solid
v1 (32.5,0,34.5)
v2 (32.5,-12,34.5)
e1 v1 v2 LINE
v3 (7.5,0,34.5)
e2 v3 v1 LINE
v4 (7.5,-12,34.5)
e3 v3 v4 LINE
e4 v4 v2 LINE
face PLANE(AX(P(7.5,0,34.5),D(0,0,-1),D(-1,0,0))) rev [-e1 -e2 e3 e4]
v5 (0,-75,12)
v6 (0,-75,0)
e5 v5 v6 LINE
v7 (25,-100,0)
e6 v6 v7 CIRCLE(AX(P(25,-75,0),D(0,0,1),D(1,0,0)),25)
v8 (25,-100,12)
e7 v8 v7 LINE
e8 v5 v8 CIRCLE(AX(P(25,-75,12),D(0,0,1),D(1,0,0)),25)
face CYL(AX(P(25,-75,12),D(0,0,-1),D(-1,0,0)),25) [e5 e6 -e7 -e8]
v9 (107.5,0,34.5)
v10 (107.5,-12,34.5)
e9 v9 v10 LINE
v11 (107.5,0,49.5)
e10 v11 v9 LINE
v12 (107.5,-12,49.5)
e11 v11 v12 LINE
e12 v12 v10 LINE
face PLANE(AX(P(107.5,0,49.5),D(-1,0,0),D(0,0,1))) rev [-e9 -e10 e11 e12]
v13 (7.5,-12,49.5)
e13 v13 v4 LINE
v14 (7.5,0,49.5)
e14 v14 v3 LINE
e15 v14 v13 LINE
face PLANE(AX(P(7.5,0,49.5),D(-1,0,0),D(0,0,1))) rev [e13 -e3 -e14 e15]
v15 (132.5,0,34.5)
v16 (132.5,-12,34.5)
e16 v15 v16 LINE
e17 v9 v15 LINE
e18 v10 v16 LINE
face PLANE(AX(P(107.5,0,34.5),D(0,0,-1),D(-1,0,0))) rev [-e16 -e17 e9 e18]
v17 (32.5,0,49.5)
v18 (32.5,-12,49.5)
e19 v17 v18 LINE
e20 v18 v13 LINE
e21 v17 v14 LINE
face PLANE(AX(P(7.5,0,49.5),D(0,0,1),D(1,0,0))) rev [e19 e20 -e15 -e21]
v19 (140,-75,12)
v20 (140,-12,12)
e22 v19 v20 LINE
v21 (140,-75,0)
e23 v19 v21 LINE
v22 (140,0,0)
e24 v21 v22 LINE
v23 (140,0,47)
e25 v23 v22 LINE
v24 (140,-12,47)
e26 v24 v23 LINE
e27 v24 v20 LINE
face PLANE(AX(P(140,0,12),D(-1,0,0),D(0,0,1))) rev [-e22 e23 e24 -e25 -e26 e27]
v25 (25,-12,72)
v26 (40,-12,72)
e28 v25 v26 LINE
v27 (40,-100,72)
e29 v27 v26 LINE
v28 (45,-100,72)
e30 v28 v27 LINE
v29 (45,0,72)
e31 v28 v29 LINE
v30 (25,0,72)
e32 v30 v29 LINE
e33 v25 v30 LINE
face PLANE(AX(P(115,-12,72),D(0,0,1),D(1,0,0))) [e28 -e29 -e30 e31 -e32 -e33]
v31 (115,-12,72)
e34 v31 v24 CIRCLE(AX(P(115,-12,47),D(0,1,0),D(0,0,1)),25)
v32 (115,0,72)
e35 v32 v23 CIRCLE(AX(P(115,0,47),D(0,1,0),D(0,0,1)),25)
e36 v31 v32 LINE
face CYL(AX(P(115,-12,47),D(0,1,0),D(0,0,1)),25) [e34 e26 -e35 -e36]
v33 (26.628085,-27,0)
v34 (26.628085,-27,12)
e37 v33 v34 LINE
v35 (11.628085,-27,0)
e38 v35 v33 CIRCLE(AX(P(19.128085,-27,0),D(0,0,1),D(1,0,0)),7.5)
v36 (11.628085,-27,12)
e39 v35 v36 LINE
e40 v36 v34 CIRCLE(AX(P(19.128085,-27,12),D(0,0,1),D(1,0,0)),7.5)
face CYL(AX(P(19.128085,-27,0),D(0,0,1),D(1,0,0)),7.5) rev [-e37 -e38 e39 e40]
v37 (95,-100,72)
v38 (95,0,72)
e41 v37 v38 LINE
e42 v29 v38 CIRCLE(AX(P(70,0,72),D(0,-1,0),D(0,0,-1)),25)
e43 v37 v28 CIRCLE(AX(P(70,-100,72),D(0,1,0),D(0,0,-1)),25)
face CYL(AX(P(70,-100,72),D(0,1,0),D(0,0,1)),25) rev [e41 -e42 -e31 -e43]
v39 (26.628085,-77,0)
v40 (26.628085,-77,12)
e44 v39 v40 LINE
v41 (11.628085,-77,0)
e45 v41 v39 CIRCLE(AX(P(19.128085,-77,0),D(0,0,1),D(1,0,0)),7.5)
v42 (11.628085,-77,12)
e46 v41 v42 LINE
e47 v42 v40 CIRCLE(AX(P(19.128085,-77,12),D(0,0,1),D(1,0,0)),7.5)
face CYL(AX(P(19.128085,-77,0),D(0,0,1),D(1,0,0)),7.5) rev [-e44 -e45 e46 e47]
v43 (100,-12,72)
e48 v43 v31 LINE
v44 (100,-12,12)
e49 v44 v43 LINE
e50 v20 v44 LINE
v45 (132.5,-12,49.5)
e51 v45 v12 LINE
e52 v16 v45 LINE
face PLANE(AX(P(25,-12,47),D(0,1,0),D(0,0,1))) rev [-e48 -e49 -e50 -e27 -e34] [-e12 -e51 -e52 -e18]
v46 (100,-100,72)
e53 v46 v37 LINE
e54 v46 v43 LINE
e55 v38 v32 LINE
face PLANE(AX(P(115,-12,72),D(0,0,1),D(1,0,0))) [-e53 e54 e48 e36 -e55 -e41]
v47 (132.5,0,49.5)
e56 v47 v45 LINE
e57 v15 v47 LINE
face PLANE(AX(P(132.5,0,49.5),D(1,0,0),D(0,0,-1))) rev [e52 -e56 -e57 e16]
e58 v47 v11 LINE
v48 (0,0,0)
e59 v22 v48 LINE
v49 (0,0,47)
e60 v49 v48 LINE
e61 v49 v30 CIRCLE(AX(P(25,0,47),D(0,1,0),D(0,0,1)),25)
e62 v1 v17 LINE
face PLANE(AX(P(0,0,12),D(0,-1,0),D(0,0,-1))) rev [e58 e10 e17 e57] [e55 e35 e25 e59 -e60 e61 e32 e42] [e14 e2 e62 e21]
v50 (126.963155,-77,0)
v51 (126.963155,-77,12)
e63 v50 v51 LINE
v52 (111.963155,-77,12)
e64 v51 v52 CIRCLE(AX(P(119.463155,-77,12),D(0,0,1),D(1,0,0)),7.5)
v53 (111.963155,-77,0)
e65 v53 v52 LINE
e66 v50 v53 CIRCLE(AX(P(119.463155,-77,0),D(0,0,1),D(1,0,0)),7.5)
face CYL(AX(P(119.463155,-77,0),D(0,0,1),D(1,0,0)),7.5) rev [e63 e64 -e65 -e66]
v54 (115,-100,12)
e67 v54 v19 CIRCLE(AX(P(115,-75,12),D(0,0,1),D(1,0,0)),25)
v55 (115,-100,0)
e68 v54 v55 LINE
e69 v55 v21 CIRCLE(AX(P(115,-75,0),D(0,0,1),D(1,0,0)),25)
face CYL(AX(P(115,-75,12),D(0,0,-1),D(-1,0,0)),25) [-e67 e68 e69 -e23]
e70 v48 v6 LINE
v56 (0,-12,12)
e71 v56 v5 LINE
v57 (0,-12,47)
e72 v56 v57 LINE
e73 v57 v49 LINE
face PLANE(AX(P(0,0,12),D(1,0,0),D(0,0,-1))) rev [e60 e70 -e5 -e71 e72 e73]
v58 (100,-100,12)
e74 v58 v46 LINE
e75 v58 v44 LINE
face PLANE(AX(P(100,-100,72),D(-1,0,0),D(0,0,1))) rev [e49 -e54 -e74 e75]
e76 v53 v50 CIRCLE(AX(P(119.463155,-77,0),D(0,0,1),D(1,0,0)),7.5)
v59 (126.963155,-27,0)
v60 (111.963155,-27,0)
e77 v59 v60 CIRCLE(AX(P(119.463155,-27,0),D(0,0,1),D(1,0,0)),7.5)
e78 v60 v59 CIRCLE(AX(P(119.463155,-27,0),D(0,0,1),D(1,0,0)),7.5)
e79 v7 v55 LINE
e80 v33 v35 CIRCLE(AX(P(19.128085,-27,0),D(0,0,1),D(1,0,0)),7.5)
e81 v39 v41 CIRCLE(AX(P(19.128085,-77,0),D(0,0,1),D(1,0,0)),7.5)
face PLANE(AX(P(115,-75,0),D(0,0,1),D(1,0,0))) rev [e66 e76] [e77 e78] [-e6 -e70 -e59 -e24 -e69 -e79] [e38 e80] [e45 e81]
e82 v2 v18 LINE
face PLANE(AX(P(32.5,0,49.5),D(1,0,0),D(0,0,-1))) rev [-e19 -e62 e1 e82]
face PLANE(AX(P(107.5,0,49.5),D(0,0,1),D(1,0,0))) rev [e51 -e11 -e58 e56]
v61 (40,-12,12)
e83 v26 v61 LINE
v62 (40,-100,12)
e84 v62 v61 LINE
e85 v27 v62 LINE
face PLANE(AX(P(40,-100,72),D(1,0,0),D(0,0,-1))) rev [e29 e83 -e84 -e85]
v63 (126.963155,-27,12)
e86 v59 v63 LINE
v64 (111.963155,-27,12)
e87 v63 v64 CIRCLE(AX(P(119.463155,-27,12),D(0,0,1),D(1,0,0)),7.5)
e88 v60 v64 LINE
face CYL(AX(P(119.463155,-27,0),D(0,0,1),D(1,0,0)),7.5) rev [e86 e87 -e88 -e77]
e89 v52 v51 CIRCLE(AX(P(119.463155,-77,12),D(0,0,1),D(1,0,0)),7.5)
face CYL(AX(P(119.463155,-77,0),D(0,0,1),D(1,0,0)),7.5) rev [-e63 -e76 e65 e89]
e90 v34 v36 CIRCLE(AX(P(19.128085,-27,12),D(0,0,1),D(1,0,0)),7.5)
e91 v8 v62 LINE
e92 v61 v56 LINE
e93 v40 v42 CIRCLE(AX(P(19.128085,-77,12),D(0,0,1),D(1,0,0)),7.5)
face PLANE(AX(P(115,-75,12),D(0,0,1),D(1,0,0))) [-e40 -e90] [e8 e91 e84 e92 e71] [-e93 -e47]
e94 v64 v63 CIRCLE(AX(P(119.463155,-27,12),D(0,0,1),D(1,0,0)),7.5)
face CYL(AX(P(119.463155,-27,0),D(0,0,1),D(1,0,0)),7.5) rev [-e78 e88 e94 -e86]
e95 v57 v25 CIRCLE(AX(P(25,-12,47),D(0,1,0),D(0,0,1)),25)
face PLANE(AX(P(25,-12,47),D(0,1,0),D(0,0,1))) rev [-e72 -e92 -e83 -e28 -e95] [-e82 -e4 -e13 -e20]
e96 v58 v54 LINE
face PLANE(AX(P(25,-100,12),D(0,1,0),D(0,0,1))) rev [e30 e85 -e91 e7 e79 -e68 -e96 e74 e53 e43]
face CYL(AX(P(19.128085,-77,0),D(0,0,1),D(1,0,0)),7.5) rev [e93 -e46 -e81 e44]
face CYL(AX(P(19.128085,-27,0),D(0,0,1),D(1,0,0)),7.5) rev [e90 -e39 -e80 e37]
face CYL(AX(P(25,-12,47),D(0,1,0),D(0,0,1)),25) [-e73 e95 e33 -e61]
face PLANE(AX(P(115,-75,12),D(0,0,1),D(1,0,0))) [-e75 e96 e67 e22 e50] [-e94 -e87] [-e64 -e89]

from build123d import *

# Parameters (mm, degrees)
BASE_PLATE_DEPTH         = 12
SIDE_FLANGE_DEPTH        = 12
BOSS_88MM_DEPTH          = 88
CURVED_START             = -12
CURVED_CUT_DEPTH         = 12
SLOT_A_SKETCH_22_5X7_5_W = 25
SLOT_A_SKETCH_22_5X7_5_H = 15
SLOT_A_22_5X7_5_DEPTH    = 12
SLOT_B_SKETCH_7_5X22_5_W = 25
SLOT_B_SKETCH_7_5X22_5_H = 15
SLOT_B_7_5X22_5_DEPTH    = 12
HOLE_A_SKETCH_15_R       = 7.5
HOLE_A_15_DEPTH          = 12
HOLE_B_SKETCH_15_R       = 7.5
HOLE_B_15_DEPTH          = 12


with BuildPart() as part:
    # Base Plate Sketch → Base Plate (new body)
    with BuildSketch(Plane.XY):
        with BuildLine():
            Line((0, 0), (0, -75))
            ThreePointArc((0, -75), (7.32233047, -92.67766953), (25, -100))
            Line((25, -100), (115, -100))
            ThreePointArc((115, -100), (132.67766953, -92.67766953), (140, -75))
            Line((140, -75), (140, 0))
            Line((140, 0), (0, 0))
        make_face()
    extrude(amount=BASE_PLATE_DEPTH)

    # Side Flange Sketch → Side Flange (add)
    with BuildSketch(Plane(origin=(0, 0, 0), x_dir=(1, 0, 0), z_dir=(0, 1, 0))):
        with BuildLine():
            Line((140, -12), (140, -47))
            ThreePointArc((140, -47), (132.67766953, -64.67766953), (115, -72))
            Line((115, -72), (25, -72))
            ThreePointArc((25, -72), (7.32233047, -64.67766953), (0, -47))
            Line((0, -47), (0, -12))
            Line((0, -12), (140, -12))
        make_face()
    extrude(amount=-SIDE_FLANGE_DEPTH)

    # Boss Profile Sketch → Boss 88mm (add)
    with BuildSketch(Plane.XZ.offset(12)):
        with BuildLine():
            Line((95, 72), (100, 72))
            Line((100, 72), (100, 12))
            Line((100, 12), (40, 12))
            Line((40, 12), (40, 72))
            Line((40, 72), (45, 72))
            ThreePointArc((45, 72), (70, 47), (95, 72))
        make_face()
    extrude(amount=BOSS_88MM_DEPTH)

    # Curved Cut Sketch → Curved Cut (cut)
    with BuildSketch(Plane.XZ.offset(12).offset(CURVED_START)):
        with BuildLine():
            Line((45, 72), (95, 72))
            ThreePointArc((95, 72), (70, 47), (45, 72))
        make_face()
    extrude(amount=CURVED_CUT_DEPTH, mode=Mode.SUBTRACT)

    # Slot A Sketch 22.5x7.5 → Slot A 22.5x7.5 (cut)
    with BuildSketch(Plane(origin=(0, -12, 0), x_dir=(-1, 0, 0), z_dir=(0, -1, 0))):
        with Locations((-120, -42)):
            Rectangle(SLOT_A_SKETCH_22_5X7_5_W, SLOT_A_SKETCH_22_5X7_5_H)
    extrude(amount=-SLOT_A_22_5X7_5_DEPTH, mode=Mode.SUBTRACT)

    # Slot B Sketch 7.5x22.5 → Slot B 7.5x22.5 (cut)
    with BuildSketch(Plane(origin=(0, -12, 0), x_dir=(-1, 0, 0), z_dir=(0, -1, 0))):
        with Locations((-20, -42)):
            Rectangle(SLOT_B_SKETCH_7_5X22_5_W, SLOT_B_SKETCH_7_5X22_5_H)
    extrude(amount=-SLOT_B_7_5X22_5_DEPTH, mode=Mode.SUBTRACT)

    # Hole A Sketch Ø15 → Hole A Ø15 (cut)
    with BuildSketch(Plane.XY.offset(12)):
        with Locations((119.463154548, -27)):
            Circle(HOLE_A_SKETCH_15_R)
        with Locations((119.463154548, -77)):
            Circle(HOLE_A_SKETCH_15_R)
    extrude(amount=-HOLE_A_15_DEPTH, mode=Mode.SUBTRACT)

    # Hole B Sketch Ø15 → Hole B Ø15 (cut)
    with BuildSketch(Plane.XY.offset(12)):
        with Locations((19.128084721, -27)):
            Circle(HOLE_B_SKETCH_15_R)
        with Locations((19.128084721, -77)):
            Circle(HOLE_B_SKETCH_15_R)
    extrude(amount=-HOLE_B_15_DEPTH, mode=Mode.SUBTRACT)


solid = part.part
